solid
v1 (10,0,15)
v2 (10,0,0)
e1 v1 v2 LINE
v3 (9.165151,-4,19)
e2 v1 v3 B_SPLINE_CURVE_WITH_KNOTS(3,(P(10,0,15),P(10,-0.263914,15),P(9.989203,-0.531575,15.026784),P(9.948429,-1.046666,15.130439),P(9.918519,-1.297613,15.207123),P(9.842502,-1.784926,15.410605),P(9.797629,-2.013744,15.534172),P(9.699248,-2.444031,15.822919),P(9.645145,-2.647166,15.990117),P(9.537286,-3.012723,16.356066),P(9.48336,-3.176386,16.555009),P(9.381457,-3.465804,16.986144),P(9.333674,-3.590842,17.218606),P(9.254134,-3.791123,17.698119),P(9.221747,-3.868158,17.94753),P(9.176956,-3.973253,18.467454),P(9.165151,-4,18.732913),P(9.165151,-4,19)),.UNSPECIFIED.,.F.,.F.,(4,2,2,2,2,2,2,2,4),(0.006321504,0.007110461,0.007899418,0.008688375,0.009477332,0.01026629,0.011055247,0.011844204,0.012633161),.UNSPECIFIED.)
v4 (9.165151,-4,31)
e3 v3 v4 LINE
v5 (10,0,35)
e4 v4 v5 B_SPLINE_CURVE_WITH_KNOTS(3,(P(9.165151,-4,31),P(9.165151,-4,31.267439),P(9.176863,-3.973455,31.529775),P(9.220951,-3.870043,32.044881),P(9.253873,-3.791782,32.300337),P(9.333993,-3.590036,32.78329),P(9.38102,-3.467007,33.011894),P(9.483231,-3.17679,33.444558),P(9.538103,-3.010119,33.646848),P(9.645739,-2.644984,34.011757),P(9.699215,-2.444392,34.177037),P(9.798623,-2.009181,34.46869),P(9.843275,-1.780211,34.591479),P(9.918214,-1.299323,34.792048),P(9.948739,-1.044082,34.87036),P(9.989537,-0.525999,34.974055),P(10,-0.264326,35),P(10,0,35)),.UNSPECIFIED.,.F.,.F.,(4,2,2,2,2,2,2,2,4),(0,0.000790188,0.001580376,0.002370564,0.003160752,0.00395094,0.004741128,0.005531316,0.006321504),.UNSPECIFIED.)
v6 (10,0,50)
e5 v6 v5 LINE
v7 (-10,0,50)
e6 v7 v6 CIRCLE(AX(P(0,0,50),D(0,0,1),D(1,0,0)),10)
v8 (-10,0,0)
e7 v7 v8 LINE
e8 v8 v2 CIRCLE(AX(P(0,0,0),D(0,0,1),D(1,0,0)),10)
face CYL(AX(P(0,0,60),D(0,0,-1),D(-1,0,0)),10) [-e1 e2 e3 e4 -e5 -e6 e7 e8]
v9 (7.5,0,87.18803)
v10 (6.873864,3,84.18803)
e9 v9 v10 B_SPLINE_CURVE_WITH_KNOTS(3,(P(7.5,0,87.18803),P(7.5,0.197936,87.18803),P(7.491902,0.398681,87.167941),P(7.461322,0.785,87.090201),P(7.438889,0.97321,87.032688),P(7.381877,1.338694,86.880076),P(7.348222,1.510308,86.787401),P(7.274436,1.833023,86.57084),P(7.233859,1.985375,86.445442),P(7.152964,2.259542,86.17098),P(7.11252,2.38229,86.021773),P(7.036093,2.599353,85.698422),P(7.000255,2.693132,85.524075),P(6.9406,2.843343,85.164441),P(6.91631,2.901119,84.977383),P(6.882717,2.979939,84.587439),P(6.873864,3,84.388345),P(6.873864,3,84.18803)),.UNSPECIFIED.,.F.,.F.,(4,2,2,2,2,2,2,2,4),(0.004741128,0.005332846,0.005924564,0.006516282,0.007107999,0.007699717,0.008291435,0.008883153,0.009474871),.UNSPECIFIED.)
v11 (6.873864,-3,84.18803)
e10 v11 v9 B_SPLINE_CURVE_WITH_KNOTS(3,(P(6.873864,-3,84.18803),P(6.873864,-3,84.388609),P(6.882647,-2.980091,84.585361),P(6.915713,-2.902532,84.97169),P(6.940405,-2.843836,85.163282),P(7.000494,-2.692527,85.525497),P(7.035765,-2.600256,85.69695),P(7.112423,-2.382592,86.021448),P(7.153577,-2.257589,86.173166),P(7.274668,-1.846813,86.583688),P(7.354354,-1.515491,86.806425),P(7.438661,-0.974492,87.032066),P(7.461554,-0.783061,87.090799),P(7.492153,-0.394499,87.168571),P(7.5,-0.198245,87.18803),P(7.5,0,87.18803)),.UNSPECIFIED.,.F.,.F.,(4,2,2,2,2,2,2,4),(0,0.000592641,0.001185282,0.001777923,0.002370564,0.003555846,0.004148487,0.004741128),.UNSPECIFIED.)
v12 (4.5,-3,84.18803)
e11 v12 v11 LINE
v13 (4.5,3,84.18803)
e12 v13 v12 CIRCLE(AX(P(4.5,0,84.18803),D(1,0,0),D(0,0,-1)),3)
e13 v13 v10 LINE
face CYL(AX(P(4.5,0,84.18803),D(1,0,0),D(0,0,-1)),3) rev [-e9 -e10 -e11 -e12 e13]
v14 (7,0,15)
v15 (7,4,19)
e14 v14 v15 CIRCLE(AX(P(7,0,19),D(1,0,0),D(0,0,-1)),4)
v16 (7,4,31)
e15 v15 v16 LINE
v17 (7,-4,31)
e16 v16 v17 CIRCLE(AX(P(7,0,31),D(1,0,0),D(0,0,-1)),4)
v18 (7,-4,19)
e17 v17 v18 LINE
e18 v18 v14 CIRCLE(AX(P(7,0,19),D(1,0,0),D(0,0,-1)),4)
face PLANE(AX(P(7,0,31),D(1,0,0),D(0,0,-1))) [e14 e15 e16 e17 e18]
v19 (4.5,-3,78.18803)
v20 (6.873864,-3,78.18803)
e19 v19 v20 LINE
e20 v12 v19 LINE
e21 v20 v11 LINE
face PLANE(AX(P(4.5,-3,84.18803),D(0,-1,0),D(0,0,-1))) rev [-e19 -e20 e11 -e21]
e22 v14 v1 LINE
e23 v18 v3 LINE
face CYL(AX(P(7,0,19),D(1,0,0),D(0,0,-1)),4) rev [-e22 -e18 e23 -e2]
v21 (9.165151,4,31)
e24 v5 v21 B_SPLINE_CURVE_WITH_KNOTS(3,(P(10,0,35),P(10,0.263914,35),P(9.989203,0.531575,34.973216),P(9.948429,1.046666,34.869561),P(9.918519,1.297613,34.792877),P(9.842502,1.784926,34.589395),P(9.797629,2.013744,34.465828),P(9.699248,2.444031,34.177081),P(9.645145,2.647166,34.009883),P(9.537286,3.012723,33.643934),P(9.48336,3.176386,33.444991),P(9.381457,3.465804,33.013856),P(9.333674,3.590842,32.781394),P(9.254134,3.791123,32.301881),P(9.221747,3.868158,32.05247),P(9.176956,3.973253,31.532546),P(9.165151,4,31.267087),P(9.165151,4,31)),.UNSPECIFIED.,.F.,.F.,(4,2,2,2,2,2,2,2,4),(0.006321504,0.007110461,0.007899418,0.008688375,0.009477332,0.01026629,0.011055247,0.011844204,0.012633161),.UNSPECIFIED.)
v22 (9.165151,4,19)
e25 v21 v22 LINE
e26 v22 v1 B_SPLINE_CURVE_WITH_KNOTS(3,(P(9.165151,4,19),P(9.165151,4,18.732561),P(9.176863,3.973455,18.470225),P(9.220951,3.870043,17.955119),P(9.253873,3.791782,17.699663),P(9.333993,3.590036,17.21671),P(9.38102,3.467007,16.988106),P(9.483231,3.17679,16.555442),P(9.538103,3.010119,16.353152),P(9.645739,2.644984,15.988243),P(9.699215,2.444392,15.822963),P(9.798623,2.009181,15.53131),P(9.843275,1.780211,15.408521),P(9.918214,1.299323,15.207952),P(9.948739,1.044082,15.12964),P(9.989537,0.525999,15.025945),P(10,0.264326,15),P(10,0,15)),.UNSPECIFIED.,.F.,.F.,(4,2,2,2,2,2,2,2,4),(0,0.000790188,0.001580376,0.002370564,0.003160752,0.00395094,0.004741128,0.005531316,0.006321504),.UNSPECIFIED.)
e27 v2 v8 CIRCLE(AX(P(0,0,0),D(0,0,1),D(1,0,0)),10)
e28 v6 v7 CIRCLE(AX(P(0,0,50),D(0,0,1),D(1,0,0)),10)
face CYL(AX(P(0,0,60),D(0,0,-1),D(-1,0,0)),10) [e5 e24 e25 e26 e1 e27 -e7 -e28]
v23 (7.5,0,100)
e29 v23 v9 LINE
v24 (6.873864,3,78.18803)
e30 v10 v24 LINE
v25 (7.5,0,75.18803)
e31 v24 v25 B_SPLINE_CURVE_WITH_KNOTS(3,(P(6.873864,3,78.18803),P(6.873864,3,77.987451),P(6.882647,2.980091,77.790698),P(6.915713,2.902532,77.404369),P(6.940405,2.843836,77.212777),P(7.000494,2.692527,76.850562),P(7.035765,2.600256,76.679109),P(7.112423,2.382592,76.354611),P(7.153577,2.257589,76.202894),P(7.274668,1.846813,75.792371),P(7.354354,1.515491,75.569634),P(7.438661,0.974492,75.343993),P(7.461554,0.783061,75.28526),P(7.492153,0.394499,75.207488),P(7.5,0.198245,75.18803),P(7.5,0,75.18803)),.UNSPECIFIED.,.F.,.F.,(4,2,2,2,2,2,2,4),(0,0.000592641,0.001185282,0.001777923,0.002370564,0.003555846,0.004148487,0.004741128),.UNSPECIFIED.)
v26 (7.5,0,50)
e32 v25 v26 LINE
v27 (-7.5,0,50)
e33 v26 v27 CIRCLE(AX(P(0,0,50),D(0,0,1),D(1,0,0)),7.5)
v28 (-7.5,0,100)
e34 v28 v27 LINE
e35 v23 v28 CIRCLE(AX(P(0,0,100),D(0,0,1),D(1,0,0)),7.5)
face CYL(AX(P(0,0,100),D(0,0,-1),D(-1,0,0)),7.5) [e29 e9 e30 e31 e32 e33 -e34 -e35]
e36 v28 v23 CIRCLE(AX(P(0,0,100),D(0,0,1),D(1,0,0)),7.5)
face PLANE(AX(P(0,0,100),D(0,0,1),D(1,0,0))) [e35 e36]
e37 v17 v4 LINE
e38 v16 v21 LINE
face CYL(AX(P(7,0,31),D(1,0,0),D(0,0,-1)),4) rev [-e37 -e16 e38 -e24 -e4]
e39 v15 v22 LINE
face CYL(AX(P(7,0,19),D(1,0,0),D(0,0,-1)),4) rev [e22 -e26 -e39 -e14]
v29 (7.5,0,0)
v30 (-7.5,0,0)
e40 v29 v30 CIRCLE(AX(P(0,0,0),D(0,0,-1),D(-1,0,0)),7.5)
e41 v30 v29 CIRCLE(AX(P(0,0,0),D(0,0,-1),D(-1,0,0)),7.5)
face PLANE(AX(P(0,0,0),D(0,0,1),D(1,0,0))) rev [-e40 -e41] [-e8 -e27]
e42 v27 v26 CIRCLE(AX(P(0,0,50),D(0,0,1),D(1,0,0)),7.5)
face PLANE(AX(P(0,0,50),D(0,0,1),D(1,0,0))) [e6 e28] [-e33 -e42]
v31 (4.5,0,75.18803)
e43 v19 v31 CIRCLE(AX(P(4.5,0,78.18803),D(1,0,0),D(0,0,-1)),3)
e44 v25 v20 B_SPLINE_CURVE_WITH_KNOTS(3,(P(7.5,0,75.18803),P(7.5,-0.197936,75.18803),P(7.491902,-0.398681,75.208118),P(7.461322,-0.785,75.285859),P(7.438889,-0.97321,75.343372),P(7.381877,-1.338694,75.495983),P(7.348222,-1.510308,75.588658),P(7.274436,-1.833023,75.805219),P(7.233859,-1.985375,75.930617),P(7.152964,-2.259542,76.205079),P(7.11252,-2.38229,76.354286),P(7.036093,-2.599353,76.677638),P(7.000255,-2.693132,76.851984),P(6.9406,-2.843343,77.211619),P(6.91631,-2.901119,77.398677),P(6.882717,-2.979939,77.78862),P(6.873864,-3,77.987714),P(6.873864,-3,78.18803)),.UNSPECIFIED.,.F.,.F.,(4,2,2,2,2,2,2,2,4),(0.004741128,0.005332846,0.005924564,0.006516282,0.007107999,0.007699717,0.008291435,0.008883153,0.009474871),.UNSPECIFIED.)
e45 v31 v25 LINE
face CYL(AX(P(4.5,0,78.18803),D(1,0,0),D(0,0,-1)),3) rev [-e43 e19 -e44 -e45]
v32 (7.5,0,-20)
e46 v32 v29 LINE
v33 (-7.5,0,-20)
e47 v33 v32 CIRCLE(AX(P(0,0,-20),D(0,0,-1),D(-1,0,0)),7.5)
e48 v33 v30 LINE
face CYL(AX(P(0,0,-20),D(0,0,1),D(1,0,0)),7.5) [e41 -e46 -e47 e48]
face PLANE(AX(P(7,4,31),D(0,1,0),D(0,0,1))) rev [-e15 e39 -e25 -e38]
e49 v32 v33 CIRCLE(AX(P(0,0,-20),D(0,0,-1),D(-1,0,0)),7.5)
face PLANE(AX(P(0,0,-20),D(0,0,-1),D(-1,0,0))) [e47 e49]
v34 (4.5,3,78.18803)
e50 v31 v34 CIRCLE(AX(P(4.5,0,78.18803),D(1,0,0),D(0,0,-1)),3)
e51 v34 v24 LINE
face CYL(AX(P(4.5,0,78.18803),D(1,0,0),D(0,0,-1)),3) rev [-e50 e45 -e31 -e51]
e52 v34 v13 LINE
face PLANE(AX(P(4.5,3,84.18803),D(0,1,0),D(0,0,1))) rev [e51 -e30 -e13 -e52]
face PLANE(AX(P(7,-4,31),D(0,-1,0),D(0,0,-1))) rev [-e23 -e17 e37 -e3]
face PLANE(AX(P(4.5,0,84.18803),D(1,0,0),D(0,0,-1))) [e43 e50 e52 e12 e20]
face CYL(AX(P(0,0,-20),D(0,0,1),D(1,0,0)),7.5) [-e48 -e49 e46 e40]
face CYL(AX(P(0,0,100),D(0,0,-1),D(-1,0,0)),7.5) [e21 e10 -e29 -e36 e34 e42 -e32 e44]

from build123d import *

# Parameters (mm, degrees)
SKETCH_1_R          = 10
EXTRUDE_1_DEPTH     = 60
SKETCH_3_R          = 7.5
EXTRUDE_3_DEPTH     = 40
CUT_EXTRUDE_START   = 10
CUT_EXTRUDE_1_DEPTH = 3
CUT_EXTRUDE_START_2 = -10
SKETCH_10_R         = 10
SKETCH_10_R_2       = 7.5
CUT_EXTRUDE_3_DEPTH = 10
CUT_EXTRUDE_START_3 = 7.5
CUT_EXTRUDE_4_DEPTH = 3
EXTRUDE_START       = 20
SKETCH_14_R         = 7.5
EXTRUDE_4_DEPTH     = 20


with BuildPart() as part:
    # 草图1 → 凸台-拉伸1 (new body)
    with BuildSketch(Plane.XY):
        with Locations(Location((0, 0, 0), (0, 0, 180))):
            Circle(SKETCH_1_R)
    extrude(amount=EXTRUDE_1_DEPTH)

    # 草图3 → 凸台-拉伸3 (add)
    with BuildSketch(Plane.XY.offset(60)):
        Circle(SKETCH_3_R)
    extrude(amount=EXTRUDE_3_DEPTH)

    # 草图4 → 切除-拉伸1 (cut)
    with BuildSketch(Plane(origin=(0, 0, 0), x_dir=(0, 0, -1), z_dir=(1, 0, 0)).offset(CUT_EXTRUDE_START)):
        with BuildLine():
            Line((-31, 4), (-19, 4))
            ThreePointArc((-19, 4), (-15, 0), (-19, -4))
            Line((-19, -4), (-31, -4))
            ThreePointArc((-31, -4), (-35, 0), (-31, 4))
        make_face()
    extrude(amount=-CUT_EXTRUDE_1_DEPTH, mode=Mode.SUBTRACT)

    # 草图10 → 切除-拉伸3 (cut)
    with BuildSketch(Plane.XY.offset(60).offset(CUT_EXTRUDE_START_2)):
        Circle(SKETCH_10_R)
        Circle(SKETCH_10_R_2, mode=Mode.SUBTRACT)
    extrude(amount=CUT_EXTRUDE_3_DEPTH, mode=Mode.SUBTRACT)

    # 草图12 → 切除-拉伸4 (cut)
    with BuildSketch(Plane(origin=(0, 0, 0), x_dir=(0, 0, -1), z_dir=(1, 0, 0)).offset(CUT_EXTRUDE_START_3)):
        with BuildLine():
            Line((-84.188029656, 3), (-78.188029656, 3))
            ThreePointArc((-78.188029656, 3), (-75.188029656, 0), (-78.188029656, -3))
            Line((-78.188029656, -3), (-84.188029656, -3))
            ThreePointArc((-84.188029656, -3), (-87.188029656, 0), (-84.188029656, 3))
        make_face()
    extrude(amount=-CUT_EXTRUDE_4_DEPTH, mode=Mode.SUBTRACT)

    # 草图14 → 凸台-拉伸4 (add)
    with BuildSketch(Plane(origin=(0, 0, 0), x_dir=(-1, 0, 0), z_dir=(0, 0, -1)).offset(EXTRUDE_START)):
        with Locations(Location((0, 0, 0), (0, 0, 180))):
            Circle(SKETCH_14_R)
    extrude(amount=-EXTRUDE_4_DEPTH)


solid = part.part
